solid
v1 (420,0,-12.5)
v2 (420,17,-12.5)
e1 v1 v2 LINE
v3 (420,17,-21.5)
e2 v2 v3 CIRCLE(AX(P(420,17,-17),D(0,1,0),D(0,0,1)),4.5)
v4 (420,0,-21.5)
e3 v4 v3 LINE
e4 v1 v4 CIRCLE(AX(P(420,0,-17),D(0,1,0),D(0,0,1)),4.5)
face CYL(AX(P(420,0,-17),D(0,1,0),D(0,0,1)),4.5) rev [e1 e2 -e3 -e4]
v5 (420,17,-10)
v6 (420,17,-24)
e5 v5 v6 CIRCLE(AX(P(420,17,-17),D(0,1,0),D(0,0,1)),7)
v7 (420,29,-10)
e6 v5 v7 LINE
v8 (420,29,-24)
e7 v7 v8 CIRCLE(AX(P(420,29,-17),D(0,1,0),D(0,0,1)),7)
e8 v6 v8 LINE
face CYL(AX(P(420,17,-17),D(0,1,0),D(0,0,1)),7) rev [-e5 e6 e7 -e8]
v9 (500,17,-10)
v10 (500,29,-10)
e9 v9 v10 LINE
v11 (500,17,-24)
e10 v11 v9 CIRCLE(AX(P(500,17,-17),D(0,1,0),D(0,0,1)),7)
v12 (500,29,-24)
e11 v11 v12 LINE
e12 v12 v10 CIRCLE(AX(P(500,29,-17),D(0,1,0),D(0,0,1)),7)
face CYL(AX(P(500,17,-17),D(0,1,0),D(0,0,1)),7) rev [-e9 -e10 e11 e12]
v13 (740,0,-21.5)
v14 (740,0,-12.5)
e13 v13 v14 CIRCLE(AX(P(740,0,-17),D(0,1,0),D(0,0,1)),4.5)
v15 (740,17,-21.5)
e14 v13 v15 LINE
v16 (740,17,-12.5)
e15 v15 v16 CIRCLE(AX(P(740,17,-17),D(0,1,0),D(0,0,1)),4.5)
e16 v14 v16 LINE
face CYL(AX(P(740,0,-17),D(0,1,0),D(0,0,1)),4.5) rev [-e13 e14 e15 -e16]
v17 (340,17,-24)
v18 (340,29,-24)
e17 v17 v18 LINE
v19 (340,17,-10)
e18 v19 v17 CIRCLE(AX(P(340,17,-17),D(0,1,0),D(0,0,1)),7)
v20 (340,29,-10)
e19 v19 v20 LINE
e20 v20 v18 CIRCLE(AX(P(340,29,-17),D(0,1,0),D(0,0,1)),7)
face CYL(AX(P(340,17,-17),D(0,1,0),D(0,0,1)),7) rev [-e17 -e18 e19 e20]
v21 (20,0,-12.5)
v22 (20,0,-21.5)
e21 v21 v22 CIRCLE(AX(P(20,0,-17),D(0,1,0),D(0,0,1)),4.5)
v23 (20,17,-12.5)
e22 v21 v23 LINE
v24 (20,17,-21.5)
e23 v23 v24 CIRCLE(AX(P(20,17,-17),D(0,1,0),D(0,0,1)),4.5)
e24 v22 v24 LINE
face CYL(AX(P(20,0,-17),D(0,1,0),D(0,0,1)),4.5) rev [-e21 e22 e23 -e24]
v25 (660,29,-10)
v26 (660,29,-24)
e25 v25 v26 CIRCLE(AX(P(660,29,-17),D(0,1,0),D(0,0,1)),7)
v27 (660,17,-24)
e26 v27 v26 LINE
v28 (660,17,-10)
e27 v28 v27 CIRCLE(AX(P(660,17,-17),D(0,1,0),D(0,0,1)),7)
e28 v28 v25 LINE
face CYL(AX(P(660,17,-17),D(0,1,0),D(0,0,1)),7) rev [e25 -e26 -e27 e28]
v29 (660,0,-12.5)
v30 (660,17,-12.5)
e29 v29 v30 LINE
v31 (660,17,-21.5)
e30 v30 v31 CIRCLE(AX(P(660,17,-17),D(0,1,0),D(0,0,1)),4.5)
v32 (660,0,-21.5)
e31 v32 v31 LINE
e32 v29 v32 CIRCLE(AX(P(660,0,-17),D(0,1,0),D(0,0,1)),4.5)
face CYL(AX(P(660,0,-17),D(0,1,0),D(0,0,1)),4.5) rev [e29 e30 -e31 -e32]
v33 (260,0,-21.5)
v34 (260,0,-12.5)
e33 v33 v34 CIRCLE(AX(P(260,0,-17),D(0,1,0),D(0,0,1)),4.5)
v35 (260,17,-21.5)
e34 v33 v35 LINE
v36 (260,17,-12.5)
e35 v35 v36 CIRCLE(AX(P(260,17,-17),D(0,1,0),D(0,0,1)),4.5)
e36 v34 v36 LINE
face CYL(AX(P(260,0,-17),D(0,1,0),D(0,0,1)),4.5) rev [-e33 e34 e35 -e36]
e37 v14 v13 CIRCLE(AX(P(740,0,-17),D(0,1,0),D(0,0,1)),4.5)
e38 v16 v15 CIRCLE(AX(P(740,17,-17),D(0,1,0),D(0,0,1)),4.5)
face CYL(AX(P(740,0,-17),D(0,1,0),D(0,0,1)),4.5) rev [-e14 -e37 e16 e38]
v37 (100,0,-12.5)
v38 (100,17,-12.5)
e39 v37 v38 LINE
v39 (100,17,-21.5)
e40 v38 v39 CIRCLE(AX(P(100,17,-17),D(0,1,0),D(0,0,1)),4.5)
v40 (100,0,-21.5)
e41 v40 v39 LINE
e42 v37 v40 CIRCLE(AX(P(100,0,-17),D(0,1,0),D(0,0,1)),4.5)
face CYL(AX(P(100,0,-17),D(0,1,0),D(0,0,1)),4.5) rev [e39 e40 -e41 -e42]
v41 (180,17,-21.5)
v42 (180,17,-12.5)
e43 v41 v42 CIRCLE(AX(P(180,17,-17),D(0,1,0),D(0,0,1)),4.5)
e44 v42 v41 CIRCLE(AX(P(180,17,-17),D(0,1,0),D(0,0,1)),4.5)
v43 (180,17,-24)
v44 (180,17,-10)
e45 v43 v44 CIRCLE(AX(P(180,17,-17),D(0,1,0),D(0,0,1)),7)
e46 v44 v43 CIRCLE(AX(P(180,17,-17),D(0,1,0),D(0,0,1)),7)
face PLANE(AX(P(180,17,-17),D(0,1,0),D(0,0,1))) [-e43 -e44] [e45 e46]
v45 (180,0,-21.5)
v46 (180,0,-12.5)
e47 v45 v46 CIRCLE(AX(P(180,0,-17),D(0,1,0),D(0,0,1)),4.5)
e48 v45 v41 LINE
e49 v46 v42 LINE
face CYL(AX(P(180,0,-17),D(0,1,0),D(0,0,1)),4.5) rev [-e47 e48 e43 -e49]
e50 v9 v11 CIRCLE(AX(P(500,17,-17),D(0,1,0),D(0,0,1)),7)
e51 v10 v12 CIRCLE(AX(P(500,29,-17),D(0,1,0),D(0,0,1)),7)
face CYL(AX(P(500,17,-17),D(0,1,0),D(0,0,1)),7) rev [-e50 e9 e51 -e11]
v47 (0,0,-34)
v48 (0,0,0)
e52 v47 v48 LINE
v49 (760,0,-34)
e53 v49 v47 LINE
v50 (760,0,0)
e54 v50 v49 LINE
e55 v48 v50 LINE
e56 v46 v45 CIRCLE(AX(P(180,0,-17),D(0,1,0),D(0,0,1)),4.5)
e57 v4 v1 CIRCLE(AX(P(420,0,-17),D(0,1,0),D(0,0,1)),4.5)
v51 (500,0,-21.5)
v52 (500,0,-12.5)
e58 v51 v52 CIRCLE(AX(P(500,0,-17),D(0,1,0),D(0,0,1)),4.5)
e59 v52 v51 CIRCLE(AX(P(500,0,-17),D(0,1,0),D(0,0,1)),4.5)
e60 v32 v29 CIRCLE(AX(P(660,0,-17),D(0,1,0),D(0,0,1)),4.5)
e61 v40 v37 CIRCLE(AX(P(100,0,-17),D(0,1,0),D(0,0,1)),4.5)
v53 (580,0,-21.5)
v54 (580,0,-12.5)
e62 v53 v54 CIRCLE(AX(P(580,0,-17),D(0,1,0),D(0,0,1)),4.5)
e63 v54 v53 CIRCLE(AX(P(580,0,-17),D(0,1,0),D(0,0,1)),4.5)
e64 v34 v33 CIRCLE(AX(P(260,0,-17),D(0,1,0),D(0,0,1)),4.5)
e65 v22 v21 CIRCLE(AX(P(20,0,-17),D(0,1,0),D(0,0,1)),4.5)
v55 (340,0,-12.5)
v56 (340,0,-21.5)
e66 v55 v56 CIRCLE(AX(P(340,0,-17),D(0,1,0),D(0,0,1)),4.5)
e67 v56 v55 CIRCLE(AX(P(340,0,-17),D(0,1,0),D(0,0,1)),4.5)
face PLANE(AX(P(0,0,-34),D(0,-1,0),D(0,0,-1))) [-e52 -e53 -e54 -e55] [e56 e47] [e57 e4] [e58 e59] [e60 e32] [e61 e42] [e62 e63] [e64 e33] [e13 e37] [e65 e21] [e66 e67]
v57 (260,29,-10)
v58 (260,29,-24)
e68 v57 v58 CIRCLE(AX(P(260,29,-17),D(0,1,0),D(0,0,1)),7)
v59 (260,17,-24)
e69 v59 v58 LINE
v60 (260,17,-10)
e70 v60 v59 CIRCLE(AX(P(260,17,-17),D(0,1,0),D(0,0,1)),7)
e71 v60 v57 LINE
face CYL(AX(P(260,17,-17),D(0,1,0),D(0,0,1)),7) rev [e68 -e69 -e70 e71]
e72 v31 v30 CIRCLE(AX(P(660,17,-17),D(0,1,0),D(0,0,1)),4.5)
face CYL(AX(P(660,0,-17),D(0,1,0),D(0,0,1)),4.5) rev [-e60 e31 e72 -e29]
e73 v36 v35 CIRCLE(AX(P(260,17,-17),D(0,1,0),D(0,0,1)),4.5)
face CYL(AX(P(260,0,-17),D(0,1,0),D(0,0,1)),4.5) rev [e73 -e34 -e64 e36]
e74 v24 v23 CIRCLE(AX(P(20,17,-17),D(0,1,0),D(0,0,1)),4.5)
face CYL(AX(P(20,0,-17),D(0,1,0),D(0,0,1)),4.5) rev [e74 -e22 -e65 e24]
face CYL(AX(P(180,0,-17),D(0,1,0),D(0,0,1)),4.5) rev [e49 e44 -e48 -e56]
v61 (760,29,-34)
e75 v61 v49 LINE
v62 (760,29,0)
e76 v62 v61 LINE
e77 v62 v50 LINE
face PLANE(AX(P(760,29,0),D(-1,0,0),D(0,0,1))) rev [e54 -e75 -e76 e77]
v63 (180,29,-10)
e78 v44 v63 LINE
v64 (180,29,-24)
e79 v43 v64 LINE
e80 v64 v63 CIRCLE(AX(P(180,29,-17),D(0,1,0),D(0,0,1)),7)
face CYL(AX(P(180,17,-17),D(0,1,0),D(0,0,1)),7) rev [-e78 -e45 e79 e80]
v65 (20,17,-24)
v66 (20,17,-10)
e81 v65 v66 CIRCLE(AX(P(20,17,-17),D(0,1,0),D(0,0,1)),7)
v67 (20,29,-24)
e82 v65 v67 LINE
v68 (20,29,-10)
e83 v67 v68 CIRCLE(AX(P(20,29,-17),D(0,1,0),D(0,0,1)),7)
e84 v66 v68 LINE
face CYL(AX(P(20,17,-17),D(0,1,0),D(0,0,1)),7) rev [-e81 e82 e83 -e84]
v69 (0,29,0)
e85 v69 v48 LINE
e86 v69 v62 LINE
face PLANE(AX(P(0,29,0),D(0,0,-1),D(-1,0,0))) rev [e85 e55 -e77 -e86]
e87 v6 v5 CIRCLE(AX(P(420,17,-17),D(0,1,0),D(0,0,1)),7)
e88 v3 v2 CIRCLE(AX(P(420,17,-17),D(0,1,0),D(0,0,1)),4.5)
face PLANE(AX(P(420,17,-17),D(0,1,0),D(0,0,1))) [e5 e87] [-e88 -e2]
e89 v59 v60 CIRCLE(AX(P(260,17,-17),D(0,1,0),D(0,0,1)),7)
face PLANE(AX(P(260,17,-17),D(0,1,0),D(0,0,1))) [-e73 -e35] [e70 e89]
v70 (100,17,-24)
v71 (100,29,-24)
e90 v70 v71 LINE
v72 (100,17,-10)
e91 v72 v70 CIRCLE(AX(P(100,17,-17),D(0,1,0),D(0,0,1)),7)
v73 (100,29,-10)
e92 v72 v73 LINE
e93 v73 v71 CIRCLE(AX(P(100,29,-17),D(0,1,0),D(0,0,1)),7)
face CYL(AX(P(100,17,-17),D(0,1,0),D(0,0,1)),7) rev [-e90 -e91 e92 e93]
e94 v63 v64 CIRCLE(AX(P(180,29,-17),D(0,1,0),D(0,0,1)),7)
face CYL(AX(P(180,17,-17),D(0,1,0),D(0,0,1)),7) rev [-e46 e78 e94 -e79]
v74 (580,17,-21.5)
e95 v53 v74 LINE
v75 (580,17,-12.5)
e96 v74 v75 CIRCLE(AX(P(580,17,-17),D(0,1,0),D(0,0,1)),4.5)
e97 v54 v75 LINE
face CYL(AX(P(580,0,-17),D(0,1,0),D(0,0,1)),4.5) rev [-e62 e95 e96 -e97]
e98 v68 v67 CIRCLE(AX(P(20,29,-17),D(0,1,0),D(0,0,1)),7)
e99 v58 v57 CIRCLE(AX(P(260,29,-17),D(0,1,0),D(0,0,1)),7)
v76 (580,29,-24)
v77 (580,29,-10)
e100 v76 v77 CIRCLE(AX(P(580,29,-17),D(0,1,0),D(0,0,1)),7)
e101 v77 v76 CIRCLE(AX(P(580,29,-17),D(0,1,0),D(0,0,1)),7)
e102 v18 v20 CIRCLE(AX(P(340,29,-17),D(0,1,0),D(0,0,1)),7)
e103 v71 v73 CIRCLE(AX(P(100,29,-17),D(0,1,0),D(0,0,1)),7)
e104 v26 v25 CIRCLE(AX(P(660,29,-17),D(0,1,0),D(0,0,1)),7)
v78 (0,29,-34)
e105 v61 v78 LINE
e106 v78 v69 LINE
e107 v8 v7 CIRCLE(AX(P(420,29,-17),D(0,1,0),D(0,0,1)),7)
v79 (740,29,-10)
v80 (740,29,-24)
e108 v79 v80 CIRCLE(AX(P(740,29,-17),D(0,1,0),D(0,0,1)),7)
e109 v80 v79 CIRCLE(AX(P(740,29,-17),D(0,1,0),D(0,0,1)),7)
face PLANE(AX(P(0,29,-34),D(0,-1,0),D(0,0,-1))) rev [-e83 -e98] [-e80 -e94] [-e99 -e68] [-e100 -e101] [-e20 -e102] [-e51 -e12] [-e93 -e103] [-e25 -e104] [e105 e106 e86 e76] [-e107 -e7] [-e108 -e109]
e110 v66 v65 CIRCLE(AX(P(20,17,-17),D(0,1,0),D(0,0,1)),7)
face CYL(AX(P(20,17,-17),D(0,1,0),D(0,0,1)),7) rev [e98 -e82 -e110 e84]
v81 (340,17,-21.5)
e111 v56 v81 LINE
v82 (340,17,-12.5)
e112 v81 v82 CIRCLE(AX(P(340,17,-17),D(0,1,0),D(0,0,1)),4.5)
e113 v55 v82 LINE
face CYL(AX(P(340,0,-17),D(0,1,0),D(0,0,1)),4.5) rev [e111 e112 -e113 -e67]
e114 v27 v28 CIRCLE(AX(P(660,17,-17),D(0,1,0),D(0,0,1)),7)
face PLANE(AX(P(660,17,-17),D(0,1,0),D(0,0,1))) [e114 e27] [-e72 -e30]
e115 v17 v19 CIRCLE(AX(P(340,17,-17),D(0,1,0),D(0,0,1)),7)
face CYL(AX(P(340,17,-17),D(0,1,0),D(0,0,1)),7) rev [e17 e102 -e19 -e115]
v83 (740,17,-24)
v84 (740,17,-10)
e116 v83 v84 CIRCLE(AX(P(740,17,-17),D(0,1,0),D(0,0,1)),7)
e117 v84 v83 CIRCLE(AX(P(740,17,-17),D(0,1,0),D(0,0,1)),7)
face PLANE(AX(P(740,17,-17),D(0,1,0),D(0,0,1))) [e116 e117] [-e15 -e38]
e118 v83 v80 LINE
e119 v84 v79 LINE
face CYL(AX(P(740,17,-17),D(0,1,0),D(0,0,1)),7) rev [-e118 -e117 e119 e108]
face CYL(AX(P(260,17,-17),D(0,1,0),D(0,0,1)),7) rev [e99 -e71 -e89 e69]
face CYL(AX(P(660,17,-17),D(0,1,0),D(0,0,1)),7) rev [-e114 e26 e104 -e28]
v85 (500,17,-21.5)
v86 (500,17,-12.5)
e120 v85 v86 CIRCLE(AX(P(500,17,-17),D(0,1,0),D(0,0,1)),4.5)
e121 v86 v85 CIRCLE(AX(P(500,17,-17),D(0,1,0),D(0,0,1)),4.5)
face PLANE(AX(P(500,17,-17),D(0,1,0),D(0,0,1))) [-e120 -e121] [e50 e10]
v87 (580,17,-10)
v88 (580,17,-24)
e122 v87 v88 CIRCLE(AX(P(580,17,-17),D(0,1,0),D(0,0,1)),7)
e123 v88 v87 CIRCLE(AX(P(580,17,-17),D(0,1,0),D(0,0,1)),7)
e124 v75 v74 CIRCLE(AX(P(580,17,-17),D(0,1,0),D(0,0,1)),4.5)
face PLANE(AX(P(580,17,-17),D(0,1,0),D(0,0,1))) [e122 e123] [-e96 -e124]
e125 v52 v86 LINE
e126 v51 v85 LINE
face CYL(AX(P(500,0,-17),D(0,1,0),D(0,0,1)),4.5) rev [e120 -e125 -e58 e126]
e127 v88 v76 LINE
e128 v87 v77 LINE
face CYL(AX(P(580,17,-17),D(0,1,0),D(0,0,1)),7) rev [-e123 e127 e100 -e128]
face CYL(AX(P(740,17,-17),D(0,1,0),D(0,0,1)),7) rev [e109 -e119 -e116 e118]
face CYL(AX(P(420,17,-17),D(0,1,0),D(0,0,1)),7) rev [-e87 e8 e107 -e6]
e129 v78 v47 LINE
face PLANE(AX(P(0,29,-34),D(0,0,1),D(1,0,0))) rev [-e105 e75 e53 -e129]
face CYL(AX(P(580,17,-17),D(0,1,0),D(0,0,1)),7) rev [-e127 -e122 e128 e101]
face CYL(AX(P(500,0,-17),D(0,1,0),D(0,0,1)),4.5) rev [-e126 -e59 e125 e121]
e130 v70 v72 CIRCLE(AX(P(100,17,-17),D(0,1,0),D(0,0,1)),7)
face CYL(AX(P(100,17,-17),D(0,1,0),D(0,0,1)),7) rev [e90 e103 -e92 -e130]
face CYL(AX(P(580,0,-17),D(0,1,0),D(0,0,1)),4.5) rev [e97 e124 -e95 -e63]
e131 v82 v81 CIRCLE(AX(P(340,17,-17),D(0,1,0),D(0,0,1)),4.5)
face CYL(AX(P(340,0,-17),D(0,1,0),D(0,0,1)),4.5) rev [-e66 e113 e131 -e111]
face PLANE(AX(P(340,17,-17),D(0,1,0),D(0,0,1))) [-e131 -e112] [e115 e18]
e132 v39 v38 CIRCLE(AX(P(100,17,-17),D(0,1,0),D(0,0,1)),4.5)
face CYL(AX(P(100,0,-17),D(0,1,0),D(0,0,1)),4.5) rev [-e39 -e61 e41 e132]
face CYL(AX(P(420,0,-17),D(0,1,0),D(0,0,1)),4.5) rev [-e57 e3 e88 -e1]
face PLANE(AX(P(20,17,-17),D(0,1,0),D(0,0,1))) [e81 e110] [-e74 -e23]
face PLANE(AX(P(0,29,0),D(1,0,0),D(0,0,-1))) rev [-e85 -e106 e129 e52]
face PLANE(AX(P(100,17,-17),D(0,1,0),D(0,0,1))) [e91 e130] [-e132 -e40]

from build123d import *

# Parameters (mm, degrees)
SKETCH_1_W             = 760
SKETCH_1_H             = 34
EXTRUDE_1_DEPTH        = 29
SKETCH_2_R             = 7
CUT_EXTRUDE_1_DEPTH    = 12
SKETCH_3_R             = 4.5
CUT_EXTRUDE_2_DEPTH    = 761.950064065
PATTERN_LINEAR_1_COUNT = 10
PATTERN_LINEAR_1_PITCH = 80


with BuildPart() as part:
    # 草图1 → 拉伸1 (new body)
    with BuildSketch(Plane(origin=(0, 0, 0), x_dir=(1, 0, 0), z_dir=(0, 1, 0))):
        with Locations((380, 17)):
            Rectangle(SKETCH_1_W, SKETCH_1_H)
    extrude(amount=EXTRUDE_1_DEPTH)

    # 草图2 → 切除-拉伸1 (cut)
    with BuildSketch(Plane(origin=(0, 29, 0), x_dir=(-1, 0, 0), z_dir=(0, 1, 0))):
        with Locations(Location((-20, -17, 0), (0, 0, 90))):
            Circle(SKETCH_2_R)
    cut_extrude_1 = extrude(amount=-CUT_EXTRUDE_1_DEPTH, mode=Mode.SUBTRACT)

    # 草图3 → 切除-拉伸2 (cut, through all)
    with BuildSketch(Plane(origin=(0, 17, 0), x_dir=(-1, 0, 0), z_dir=(0, 1, 0))):
        with Locations(Location((-20, -17, 0), (0, 0, 90))):
            Circle(SKETCH_3_R)
    cut_extrude_2 = extrude(amount=-CUT_EXTRUDE_2_DEPTH, mode=Mode.SUBTRACT)

    # 阵列(线性)1: 切除-拉伸1, 切除-拉伸2 ×10
    with Locations(*[(i * PATTERN_LINEAR_1_PITCH, 0, 0) for i in range(1, PATTERN_LINEAR_1_COUNT)]):
        add(cut_extrude_1, mode=Mode.SUBTRACT)
        add(cut_extrude_2, mode=Mode.SUBTRACT)


solid = part.part
